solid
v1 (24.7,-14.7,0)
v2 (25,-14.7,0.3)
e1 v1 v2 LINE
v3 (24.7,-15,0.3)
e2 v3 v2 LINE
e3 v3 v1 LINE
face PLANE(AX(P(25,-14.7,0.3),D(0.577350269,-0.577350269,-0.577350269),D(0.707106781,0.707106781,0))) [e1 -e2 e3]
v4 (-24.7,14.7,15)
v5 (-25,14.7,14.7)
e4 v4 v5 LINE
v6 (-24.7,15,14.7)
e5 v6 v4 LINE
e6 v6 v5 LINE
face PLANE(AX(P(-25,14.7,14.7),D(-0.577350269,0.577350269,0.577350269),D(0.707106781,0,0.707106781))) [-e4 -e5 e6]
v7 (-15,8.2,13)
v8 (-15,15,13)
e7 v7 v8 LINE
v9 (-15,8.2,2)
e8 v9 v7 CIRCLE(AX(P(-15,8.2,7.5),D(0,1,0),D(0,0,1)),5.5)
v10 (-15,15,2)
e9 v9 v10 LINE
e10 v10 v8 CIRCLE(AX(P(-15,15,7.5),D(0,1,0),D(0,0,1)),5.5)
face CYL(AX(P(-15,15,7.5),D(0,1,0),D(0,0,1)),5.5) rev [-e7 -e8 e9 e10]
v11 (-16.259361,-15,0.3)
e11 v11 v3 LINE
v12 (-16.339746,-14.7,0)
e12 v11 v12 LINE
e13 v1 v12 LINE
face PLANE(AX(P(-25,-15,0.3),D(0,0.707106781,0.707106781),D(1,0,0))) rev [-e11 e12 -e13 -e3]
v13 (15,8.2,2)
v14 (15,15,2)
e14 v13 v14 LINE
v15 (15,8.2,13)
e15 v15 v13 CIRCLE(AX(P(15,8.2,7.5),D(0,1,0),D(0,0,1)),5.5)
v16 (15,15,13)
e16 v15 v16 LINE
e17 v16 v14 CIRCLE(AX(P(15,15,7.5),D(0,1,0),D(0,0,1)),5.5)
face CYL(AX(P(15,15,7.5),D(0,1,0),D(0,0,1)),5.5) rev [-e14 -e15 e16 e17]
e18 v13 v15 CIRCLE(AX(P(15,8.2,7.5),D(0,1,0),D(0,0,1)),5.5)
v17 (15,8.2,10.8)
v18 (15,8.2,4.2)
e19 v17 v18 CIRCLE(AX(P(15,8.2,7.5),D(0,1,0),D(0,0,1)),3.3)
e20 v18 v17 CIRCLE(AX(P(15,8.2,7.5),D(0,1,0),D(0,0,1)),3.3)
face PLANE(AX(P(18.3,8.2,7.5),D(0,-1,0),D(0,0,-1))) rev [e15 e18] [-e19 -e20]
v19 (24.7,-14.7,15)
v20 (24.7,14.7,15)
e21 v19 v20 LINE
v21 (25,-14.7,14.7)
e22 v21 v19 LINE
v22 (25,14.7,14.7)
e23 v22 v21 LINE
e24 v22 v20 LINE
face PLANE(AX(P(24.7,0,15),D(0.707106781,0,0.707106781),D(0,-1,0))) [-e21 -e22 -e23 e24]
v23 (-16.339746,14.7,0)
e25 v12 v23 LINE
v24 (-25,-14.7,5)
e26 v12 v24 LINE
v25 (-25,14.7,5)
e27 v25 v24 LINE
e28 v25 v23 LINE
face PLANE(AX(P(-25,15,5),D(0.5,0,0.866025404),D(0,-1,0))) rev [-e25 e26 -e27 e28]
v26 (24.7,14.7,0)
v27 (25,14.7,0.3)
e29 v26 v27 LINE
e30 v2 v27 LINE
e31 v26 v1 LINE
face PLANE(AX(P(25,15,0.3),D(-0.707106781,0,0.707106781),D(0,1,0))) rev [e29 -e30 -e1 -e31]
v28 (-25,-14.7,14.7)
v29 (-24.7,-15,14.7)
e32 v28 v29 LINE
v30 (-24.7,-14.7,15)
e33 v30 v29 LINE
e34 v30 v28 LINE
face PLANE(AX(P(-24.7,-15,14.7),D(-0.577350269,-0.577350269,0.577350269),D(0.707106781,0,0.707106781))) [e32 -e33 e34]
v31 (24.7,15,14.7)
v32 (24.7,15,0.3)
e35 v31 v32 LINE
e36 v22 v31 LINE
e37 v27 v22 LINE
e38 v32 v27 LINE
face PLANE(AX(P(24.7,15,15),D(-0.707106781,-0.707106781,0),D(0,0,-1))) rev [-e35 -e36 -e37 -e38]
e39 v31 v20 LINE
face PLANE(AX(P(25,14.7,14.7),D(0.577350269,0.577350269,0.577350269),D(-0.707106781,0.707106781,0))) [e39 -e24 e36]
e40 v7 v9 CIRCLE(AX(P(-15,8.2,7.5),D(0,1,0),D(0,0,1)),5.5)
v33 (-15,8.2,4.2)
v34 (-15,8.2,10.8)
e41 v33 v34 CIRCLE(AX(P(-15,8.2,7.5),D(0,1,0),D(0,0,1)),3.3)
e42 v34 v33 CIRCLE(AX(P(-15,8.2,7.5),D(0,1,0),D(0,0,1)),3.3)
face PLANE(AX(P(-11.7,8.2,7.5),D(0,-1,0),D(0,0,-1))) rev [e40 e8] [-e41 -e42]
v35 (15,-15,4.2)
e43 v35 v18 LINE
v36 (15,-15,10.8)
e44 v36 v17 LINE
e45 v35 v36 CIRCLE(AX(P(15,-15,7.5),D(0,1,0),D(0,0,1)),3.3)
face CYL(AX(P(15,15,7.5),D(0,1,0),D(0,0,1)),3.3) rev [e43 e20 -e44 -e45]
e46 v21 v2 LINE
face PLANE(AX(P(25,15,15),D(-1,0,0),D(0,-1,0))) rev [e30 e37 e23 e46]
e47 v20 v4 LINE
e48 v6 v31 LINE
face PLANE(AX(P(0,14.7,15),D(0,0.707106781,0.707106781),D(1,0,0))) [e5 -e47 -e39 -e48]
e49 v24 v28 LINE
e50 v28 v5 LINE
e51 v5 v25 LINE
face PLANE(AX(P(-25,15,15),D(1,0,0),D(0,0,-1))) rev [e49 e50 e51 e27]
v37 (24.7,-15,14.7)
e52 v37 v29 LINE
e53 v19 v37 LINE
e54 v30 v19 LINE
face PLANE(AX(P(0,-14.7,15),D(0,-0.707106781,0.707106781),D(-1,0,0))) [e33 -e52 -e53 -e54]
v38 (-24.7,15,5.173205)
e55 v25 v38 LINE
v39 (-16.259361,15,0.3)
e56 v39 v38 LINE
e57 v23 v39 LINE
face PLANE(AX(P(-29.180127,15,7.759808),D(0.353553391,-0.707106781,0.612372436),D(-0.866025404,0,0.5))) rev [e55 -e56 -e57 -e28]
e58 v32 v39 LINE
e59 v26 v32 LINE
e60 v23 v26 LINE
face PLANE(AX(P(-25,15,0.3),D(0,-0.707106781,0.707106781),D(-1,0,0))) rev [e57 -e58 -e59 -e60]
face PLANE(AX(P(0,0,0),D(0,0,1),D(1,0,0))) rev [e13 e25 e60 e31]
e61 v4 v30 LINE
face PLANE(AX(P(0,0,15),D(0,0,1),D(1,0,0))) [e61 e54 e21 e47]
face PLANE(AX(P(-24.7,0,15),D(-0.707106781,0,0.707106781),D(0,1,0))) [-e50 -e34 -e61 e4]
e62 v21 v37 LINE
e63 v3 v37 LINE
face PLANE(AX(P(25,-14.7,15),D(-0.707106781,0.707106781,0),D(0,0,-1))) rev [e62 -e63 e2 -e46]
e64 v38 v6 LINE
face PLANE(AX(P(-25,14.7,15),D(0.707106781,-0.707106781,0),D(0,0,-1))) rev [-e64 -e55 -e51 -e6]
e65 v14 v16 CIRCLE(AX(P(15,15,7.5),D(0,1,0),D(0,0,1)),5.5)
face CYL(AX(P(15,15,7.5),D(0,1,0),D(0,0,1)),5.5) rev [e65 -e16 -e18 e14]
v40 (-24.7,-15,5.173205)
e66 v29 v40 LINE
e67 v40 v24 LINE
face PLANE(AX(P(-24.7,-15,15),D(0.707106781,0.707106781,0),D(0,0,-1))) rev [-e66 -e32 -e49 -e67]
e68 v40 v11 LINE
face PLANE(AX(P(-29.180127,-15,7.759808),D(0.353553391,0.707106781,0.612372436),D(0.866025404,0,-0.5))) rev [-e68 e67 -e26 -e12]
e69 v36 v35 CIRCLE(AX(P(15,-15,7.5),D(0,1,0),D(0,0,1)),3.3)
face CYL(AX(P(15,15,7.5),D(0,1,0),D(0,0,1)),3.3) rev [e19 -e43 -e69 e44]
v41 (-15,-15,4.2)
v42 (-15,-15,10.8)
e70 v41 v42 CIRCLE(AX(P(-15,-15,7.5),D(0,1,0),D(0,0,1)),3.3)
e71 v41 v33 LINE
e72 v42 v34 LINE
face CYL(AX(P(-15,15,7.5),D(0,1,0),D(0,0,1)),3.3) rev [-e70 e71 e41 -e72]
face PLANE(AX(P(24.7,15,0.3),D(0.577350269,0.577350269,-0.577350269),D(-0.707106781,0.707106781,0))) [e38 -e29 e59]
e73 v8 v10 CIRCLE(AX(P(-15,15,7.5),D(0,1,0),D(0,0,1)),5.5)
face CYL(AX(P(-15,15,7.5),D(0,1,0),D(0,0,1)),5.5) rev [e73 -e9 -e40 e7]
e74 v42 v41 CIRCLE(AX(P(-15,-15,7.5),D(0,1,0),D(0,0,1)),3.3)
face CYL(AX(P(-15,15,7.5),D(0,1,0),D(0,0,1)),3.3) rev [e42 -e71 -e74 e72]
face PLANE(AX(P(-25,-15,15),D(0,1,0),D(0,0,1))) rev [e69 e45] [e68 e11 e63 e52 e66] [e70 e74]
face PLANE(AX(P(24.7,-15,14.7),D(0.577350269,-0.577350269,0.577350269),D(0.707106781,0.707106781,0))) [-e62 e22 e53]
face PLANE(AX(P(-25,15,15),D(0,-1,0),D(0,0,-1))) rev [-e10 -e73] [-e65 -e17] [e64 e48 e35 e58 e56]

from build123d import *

# Parameters (mm, degrees)
SKETCH_1_W                = 50
SKETCH_1_H                = 30
EXTRUDE_1_DEPTH           = 15
HOLE_WIZARD_1_D           = 6.6
HOLE_WIZARD_1_CBORE_D     = 11
HOLE_WIZARD_1_CBORE_DEPTH = 6.8
CHAMFER_1_SIZE            = 5
CHAMFER_1_SIZE2           = 8.660254038
CHAMFER_2_SIZE            = 0.3


with BuildPart() as part:
    # 草图1 → 凸台-拉伸1 (new body)
    with BuildSketch(Plane.XY):
        Rectangle(SKETCH_1_W, SKETCH_1_H)
    extrude(amount=EXTRUDE_1_DEPTH)

    # 打孔尺寸根据内六角圆柱头螺钉的类型1 (through all)
    with Locations(Plane(origin=(0, 15, 0), x_dir=(1, 0, 0), z_dir=(0, 1, 0))):
        with Locations((-15, -7.5), (15, -7.5)):
            CounterBoreHole(HOLE_WIZARD_1_D / 2, HOLE_WIZARD_1_CBORE_D / 2, HOLE_WIZARD_1_CBORE_DEPTH)

    # 倒角1
    chamfer_1_edges = [part.edges().sort_by_distance(p)[0] for p in [
        (-25, 0, 0),
    ]]
    chamfer_1_side = [part.faces().sort_by_distance(p)[0] for p in [
        (-25, 0, 7.5),
    ]]
    chamfer(chamfer_1_edges, length=CHAMFER_1_SIZE, length2=CHAMFER_1_SIZE2, reference=chamfer_1_side[0])

    # 倒角2
    chamfer_2_edges = [part.edges().sort_by_distance(p)[0] for p in [
        (-25, 0, 15),
        (0, -15, 15),
        (4.330127019, -15, 0),
        (-20.669872981, -15, 2.5),
        (-20.669872981, 15, 2.5),
        (25, 0, 15),
        (4.330127019, 15, 0),
        (25, 0, 0),
        (0, 15, 15),
        (25, -15, 7.5),
        (-25, -15, 10),
        (-25, 15, 10),
        (25, 15, 7.5),
    ]]
    chamfer(chamfer_2_edges, length=CHAMFER_2_SIZE)


solid = part.part
